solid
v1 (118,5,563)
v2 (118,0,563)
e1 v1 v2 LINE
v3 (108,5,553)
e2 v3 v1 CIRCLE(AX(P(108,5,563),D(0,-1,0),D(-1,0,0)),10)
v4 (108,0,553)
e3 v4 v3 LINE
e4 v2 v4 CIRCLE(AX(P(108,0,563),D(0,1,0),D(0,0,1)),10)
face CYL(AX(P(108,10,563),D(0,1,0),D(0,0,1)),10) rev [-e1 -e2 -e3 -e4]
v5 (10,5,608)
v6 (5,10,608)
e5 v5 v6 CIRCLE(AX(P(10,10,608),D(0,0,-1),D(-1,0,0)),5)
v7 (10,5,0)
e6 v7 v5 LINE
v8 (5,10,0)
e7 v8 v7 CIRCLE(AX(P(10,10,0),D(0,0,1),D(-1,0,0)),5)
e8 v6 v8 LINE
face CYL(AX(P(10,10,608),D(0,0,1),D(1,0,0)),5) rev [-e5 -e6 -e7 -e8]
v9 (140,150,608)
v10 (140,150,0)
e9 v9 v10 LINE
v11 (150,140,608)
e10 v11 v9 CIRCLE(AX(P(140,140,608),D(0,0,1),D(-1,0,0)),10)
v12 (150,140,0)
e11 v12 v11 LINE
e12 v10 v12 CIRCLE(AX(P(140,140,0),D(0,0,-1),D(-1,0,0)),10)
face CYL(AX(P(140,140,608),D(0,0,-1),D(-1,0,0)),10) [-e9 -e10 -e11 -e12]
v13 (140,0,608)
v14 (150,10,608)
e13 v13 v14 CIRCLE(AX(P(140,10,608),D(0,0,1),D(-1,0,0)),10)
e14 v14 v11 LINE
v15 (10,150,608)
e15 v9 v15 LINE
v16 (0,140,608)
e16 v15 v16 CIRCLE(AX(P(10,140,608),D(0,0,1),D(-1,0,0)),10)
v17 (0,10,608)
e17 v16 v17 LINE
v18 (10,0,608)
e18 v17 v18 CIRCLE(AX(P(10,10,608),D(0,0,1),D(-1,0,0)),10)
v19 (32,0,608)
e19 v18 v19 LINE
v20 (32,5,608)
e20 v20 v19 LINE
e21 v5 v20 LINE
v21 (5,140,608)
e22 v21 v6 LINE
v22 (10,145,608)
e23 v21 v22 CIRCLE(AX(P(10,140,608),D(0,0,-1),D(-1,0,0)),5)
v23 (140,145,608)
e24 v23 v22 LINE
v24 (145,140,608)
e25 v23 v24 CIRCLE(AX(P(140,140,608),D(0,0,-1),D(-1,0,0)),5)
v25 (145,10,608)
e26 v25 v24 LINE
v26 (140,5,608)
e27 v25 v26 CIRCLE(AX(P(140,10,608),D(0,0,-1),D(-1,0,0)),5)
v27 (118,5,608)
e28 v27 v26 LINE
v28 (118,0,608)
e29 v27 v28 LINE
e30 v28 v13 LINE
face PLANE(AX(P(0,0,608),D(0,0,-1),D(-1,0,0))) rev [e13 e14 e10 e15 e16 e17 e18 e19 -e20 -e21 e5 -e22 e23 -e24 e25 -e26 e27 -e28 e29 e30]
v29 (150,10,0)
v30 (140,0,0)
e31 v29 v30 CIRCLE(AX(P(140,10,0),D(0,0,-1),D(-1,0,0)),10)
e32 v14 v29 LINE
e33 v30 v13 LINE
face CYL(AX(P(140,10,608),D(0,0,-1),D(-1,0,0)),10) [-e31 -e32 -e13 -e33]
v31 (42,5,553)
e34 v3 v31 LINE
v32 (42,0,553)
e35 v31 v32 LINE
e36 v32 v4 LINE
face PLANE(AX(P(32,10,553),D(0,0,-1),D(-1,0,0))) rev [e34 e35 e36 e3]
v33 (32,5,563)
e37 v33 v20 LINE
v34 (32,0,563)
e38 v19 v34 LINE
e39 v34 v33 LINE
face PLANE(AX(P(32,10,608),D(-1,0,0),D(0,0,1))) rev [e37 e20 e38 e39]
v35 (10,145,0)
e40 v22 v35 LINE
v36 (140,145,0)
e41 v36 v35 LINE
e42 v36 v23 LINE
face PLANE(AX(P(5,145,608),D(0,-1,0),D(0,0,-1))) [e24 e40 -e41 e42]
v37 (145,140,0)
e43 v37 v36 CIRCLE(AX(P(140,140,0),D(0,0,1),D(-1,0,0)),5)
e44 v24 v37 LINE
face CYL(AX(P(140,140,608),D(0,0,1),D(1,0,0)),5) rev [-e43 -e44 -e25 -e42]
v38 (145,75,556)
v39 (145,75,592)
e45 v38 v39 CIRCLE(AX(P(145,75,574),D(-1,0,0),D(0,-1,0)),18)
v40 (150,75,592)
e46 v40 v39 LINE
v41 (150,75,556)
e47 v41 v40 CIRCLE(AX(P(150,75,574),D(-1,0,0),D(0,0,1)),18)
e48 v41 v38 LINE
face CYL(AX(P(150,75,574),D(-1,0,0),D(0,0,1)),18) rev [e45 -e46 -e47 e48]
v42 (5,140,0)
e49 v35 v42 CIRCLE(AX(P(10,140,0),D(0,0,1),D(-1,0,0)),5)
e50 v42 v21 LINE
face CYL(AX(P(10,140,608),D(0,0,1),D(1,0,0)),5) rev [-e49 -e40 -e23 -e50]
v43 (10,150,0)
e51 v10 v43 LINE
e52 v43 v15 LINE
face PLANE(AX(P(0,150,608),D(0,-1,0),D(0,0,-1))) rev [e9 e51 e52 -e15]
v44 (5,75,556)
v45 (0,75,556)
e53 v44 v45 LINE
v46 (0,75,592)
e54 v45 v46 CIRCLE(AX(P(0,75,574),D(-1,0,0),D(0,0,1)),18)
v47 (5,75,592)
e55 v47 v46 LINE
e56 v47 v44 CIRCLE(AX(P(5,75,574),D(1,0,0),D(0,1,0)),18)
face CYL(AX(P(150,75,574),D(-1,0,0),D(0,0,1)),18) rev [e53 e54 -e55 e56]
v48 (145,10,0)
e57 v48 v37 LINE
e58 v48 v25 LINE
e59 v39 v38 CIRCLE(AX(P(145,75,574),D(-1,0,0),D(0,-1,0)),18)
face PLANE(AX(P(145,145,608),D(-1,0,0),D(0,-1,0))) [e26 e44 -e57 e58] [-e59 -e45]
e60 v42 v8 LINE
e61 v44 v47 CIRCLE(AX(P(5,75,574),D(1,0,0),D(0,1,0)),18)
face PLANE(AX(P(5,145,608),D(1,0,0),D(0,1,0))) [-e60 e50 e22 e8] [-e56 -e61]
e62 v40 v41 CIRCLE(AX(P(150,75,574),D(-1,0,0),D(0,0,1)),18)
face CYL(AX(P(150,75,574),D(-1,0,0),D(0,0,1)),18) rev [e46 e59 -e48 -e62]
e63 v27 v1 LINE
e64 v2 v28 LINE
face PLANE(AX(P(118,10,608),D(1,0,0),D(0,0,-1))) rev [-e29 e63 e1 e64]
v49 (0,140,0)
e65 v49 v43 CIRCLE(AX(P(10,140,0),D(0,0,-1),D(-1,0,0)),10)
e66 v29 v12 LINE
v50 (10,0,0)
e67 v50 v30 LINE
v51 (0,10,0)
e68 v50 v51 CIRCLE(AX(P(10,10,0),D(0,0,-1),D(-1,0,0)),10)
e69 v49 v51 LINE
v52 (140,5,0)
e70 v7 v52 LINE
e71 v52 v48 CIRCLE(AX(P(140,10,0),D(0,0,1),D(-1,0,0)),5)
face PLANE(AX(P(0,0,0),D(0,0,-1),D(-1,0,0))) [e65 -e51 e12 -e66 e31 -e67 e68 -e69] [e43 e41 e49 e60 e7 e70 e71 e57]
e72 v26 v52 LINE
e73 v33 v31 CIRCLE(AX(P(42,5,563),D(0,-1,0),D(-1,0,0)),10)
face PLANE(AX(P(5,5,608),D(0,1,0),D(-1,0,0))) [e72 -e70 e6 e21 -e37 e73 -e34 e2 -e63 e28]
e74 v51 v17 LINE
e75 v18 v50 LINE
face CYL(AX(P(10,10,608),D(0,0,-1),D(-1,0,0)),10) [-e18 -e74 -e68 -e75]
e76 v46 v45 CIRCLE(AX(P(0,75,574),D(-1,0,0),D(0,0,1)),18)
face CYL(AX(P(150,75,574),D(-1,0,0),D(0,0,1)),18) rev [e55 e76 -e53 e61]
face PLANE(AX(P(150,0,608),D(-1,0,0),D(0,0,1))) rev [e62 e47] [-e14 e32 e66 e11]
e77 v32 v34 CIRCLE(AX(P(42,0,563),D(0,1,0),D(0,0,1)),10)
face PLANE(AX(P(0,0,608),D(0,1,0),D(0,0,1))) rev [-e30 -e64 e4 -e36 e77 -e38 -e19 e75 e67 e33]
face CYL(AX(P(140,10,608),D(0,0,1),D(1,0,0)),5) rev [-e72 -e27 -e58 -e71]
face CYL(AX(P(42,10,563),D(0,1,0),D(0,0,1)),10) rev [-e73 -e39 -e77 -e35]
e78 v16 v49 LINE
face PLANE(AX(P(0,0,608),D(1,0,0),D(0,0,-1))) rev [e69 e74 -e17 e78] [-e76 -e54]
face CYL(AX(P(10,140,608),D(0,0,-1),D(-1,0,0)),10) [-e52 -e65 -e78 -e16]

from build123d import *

# Parameters (mm, degrees)
SKETCH1_W           = 150
SKETCH1_H           = 150
SKETCH1_W_2         = 140
SKETCH1_H_2         = 140
BOSS_EXTRUDE1_DEPTH = 608
FILLET1_R           = 10
FILLET2_R           = 5
SKETCH2_R           = 18
CUT_EXTRUDE1_DEPTH  = 644.944096953
SKETCH3_W           = 86
SKETCH3_H           = 55
CUT_EXTRUDE2_DEPTH  = 10
FILLET3_R           = 10


with BuildPart() as part:
    # Sketch1 → Boss-Extrude1 (new body)
    with BuildSketch(Plane.XY):
        with Locations((75, 75)):
            Rectangle(SKETCH1_W, SKETCH1_H)
        with Locations((75, 75)):
            Rectangle(SKETCH1_W_2, SKETCH1_H_2, mode=Mode.SUBTRACT)
    extrude(amount=BOSS_EXTRUDE1_DEPTH)

    # Fillet1
    fillet1_edges = [part.edges().sort_by_distance(p)[0] for p in [
        (0, 150, 304),
        (150, 150, 304),
        (150, 0, 304),
        (0, 0, 304),
    ]]
    fillet(fillet1_edges, radius=FILLET1_R)

    # Fillet2
    fillet2_edges = [part.edges().sort_by_distance(p)[0] for p in [
        (5, 145, 304),
        (5, 5, 304),
        (145, 5, 304),
        (145, 145, 304),
    ]]
    fillet(fillet2_edges, radius=FILLET2_R)

    # Sketch2 → Cut-Extrude1 (cut, through all)
    with BuildSketch(Plane.ZY):
        with Locations((574, 75)):
            Circle(SKETCH2_R)
    extrude(amount=-CUT_EXTRUDE1_DEPTH, mode=Mode.SUBTRACT)

    # Sketch3 → Cut-Extrude2 (cut)
    with BuildSketch(Plane.XZ):
        with Locations((75, 580.5)):
            Rectangle(SKETCH3_W, SKETCH3_H)
    extrude(amount=-CUT_EXTRUDE2_DEPTH, mode=Mode.SUBTRACT)

    # Fillet3
    fillet3_edges = [part.edges().sort_by_distance(p)[0] for p in [
        (32, 2.5, 553),
        (118, 2.5, 553),
    ]]
    fillet(fillet3_edges, radius=FILLET3_R)


solid = part.part
